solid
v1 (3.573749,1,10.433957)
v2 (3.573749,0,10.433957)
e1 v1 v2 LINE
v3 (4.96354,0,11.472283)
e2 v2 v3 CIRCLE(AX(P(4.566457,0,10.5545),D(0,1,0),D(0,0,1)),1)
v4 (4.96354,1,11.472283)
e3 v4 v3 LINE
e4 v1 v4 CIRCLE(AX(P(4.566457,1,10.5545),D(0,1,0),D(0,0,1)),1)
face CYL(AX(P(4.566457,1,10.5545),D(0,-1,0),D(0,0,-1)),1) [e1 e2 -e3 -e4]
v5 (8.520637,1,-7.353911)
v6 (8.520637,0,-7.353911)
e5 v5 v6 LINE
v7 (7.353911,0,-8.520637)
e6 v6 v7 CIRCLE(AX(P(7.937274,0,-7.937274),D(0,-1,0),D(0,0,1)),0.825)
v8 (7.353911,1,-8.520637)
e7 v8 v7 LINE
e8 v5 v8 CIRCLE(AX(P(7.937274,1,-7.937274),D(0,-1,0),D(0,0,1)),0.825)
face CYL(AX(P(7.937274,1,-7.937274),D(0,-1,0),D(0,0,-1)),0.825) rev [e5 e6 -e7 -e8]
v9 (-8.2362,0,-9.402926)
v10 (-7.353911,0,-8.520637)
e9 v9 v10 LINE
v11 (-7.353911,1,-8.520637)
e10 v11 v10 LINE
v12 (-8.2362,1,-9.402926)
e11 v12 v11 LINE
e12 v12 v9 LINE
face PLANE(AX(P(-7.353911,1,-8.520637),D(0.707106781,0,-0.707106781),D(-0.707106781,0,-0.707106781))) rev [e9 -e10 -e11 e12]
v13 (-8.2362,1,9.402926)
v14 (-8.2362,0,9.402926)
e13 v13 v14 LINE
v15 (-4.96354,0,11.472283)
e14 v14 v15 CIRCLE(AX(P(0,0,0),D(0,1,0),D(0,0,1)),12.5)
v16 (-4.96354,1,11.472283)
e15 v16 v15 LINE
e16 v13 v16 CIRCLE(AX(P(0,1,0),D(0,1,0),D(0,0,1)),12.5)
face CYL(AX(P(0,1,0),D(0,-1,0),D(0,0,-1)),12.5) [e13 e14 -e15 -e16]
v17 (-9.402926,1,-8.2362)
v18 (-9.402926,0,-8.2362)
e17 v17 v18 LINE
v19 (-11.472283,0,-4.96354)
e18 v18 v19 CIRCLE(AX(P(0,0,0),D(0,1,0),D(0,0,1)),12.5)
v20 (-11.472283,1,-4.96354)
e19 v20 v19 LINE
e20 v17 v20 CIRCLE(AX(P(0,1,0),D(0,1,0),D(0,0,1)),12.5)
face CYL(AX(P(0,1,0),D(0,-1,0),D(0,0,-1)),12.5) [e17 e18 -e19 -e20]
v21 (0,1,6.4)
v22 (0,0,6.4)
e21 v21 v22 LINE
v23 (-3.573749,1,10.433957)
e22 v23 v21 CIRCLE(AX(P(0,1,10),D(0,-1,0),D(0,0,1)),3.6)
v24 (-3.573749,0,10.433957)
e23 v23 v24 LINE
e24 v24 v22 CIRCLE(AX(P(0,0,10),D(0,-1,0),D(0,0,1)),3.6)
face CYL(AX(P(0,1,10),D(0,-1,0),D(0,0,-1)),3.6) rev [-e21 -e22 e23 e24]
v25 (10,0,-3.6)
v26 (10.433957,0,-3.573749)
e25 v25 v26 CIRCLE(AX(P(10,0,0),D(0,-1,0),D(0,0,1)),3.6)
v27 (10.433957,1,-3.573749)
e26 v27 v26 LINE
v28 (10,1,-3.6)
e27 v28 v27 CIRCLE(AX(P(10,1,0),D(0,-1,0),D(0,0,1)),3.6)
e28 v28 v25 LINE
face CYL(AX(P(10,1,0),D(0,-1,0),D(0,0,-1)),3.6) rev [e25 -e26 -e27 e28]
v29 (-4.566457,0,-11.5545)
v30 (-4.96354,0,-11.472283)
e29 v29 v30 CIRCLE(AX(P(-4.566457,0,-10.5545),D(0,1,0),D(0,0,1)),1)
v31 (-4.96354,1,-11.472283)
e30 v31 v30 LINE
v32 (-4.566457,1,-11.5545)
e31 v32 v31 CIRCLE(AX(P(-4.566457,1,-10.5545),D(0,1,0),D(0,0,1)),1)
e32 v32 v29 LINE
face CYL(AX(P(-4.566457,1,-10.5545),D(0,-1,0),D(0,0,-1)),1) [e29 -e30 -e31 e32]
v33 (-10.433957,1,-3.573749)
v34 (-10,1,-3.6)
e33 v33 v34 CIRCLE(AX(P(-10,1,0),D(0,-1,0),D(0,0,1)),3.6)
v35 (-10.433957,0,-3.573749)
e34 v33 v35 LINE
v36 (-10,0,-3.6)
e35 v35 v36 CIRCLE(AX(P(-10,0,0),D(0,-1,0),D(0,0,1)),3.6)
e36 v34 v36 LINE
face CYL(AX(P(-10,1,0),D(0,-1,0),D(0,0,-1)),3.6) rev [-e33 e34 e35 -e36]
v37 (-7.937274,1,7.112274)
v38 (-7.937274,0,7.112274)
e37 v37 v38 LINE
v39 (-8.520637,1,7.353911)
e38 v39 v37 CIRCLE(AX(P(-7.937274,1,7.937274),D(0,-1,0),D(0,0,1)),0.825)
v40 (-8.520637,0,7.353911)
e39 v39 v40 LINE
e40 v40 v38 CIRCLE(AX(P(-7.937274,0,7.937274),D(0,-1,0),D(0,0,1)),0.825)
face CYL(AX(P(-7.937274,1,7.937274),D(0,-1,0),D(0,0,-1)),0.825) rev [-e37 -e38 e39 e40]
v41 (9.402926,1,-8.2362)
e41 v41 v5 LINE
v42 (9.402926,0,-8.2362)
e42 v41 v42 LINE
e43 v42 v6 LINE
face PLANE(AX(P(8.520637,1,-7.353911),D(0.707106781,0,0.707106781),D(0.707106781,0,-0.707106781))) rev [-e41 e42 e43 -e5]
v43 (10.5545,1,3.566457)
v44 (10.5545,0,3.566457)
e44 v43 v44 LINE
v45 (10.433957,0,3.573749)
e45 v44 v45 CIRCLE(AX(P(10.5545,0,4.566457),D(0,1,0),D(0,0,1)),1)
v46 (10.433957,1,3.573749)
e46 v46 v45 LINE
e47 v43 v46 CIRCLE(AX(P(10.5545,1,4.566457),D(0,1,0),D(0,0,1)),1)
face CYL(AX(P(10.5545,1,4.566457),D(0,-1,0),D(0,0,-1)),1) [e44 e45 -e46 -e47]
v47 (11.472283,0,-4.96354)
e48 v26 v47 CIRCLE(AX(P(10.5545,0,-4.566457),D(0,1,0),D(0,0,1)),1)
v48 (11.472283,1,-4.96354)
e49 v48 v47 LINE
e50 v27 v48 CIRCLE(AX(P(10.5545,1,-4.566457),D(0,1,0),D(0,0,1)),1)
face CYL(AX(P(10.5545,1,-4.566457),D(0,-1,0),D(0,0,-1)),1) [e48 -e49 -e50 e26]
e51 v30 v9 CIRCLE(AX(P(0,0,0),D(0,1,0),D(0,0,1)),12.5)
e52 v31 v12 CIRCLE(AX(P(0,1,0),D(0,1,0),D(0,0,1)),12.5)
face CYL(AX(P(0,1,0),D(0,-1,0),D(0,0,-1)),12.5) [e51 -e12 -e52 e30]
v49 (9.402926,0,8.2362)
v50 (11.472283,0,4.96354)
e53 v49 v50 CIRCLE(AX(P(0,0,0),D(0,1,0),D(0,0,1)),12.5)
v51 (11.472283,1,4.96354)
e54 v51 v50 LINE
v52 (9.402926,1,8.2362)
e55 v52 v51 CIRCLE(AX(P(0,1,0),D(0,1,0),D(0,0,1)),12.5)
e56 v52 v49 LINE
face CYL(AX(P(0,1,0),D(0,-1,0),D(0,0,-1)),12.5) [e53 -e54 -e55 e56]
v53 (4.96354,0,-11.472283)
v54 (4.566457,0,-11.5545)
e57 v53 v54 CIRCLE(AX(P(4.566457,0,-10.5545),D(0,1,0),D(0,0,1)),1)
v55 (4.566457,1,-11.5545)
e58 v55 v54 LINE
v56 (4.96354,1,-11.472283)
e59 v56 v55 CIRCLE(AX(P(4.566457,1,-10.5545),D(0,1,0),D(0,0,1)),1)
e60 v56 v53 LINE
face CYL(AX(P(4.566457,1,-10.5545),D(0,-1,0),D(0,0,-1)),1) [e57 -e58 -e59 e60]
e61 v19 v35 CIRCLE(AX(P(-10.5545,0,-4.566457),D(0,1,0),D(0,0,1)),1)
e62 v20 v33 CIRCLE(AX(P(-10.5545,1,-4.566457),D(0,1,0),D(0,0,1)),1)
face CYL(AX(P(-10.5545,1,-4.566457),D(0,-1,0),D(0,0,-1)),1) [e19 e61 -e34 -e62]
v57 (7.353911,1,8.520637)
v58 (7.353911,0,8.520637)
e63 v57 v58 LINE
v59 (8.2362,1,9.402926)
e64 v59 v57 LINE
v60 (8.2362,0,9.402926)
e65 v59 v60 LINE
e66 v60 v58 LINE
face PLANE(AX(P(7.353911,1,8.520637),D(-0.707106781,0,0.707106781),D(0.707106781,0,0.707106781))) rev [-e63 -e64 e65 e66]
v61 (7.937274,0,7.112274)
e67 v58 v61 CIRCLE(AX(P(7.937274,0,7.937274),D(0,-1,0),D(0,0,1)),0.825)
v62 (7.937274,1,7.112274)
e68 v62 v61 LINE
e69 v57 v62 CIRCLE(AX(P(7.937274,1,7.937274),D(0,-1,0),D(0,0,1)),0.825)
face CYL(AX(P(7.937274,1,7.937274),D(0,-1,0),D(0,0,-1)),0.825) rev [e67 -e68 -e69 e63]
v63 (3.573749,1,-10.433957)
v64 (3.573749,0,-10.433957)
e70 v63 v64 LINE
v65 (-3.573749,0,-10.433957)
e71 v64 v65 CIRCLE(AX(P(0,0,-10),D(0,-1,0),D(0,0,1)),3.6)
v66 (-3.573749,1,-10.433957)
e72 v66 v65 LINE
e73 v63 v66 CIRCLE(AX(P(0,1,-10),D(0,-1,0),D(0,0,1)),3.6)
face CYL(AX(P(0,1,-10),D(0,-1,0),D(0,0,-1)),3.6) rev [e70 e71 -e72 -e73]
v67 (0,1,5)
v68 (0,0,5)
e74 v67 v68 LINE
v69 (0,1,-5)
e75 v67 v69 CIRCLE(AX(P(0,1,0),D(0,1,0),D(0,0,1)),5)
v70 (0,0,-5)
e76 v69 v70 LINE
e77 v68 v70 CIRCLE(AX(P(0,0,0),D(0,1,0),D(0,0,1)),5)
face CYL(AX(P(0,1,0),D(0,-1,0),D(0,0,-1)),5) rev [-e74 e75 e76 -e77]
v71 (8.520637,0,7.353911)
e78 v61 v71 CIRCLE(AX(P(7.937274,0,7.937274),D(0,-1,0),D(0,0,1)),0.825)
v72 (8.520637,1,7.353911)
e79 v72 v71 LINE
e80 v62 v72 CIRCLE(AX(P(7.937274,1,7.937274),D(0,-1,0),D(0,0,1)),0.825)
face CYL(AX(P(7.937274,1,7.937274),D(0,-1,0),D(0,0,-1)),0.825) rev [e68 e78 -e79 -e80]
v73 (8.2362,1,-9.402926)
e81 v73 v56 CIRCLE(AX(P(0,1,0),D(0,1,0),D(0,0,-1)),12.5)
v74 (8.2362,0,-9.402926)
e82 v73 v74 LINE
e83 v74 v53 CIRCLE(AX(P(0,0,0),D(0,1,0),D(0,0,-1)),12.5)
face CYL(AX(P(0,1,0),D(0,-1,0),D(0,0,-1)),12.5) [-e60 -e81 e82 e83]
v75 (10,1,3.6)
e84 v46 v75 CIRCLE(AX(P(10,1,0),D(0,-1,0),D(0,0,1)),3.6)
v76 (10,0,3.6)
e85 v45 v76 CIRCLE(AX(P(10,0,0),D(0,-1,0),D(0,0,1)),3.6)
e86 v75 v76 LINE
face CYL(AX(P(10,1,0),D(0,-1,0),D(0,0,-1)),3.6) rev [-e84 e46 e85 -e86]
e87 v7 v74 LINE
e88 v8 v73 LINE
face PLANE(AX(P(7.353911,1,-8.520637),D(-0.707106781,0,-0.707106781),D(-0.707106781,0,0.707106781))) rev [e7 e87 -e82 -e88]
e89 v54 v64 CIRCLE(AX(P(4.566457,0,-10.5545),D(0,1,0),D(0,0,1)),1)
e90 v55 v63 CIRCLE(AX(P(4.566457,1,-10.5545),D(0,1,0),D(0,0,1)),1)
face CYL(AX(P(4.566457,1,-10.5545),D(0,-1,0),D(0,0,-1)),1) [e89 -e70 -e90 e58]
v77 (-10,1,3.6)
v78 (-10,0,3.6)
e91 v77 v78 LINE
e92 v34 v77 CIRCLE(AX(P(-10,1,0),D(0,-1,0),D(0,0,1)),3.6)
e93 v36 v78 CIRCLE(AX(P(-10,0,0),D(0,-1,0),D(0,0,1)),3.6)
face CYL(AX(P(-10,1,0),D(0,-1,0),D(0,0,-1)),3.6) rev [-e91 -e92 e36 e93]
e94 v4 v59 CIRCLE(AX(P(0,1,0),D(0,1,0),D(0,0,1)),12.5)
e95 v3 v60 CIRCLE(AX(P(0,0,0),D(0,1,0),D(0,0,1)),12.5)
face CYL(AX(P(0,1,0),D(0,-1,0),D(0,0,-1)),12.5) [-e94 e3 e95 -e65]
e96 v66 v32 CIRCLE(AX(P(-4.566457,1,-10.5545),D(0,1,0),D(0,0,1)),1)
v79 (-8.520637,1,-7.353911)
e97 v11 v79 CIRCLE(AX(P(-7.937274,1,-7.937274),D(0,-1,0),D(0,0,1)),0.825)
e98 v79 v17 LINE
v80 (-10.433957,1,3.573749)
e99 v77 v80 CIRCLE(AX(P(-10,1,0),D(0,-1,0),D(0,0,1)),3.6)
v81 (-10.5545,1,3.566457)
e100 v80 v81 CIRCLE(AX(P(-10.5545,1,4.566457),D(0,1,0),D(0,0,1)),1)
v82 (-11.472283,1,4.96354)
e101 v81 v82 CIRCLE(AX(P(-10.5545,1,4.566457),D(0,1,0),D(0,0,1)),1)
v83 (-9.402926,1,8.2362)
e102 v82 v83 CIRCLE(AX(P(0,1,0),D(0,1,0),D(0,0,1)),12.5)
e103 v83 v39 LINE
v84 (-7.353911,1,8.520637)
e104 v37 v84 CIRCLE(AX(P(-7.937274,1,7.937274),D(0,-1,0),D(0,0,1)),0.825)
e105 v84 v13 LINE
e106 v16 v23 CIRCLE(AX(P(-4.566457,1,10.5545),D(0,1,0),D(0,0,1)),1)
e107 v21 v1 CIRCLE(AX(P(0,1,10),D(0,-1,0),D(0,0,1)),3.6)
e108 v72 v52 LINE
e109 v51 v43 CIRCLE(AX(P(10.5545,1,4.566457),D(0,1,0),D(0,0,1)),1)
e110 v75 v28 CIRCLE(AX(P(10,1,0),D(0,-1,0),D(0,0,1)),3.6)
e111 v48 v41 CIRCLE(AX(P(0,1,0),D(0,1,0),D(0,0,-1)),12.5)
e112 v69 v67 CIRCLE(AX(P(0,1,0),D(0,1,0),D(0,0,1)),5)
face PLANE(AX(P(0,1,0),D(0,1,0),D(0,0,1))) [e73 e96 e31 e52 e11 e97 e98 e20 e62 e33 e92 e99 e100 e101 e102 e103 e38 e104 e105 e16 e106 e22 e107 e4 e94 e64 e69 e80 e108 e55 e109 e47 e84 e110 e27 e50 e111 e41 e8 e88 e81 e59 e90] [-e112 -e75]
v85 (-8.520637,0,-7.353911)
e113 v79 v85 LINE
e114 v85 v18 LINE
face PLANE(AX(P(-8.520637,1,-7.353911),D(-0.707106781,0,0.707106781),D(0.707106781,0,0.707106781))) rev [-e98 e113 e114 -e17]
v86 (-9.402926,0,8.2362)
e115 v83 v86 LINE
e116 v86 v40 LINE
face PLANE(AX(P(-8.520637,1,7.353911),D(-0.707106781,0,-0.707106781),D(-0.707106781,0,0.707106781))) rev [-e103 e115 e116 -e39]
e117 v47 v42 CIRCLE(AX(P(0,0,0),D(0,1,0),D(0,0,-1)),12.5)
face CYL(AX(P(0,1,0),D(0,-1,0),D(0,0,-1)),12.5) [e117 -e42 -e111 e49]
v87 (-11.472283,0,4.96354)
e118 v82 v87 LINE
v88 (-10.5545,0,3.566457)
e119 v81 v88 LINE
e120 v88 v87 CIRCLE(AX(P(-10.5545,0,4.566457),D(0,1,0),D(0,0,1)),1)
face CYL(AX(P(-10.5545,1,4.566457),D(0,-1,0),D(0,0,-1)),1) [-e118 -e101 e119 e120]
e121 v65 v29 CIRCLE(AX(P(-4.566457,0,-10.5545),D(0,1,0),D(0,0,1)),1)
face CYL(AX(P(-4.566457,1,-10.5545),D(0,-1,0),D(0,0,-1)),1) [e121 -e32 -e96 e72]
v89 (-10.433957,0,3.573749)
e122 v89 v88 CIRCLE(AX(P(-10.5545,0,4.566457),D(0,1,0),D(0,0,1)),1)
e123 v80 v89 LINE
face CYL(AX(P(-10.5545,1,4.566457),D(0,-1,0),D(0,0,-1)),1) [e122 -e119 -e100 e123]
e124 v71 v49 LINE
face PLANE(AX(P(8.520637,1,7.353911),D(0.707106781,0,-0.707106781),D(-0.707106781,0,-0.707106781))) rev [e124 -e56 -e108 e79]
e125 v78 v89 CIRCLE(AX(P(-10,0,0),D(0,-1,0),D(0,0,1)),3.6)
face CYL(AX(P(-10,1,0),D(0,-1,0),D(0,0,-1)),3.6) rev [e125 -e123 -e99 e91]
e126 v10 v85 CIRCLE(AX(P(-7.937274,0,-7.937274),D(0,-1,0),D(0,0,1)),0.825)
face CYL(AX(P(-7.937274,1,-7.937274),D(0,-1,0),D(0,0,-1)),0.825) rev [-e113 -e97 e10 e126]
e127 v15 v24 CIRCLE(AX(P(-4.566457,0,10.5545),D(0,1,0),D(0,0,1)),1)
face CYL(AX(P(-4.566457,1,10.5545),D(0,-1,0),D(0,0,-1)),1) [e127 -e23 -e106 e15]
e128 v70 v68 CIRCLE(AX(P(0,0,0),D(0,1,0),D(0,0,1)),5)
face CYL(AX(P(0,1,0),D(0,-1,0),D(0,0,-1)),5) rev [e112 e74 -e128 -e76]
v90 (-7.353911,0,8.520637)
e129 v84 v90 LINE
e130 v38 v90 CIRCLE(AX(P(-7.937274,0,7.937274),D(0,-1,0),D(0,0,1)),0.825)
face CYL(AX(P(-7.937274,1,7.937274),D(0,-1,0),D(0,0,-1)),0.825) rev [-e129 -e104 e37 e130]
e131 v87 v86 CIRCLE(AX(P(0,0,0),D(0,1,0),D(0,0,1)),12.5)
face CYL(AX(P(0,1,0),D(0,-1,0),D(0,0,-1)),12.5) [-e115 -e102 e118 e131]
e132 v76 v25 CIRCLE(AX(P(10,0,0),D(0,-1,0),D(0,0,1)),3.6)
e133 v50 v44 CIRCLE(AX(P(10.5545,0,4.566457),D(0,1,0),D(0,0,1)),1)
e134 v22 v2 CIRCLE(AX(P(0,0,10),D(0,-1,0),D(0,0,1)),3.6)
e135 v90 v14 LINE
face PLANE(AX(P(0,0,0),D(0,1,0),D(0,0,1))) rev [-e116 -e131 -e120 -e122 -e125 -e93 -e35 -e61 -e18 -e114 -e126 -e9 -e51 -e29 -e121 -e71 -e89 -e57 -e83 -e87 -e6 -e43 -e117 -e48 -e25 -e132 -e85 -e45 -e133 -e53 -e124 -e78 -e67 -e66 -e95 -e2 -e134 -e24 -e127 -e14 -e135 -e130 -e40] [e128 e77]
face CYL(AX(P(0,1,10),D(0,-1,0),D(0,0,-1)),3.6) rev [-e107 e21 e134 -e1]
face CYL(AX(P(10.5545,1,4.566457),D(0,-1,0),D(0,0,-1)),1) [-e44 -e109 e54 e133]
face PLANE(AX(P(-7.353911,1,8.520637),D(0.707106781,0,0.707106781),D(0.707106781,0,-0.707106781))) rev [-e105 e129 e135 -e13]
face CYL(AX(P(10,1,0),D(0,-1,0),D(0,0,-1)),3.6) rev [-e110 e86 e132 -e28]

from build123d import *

# Parameters (mm, degrees)
SKETCH4_R           = 5
BOSS_EXTRUDE1_DEPTH = 1


with BuildPart() as part:
    # Sketch4 → Boss-Extrude1 (new body)
    with BuildSketch(Plane(origin=(0, 0, 0), x_dir=(1, 0, 0), z_dir=(0, 1, 0))):
        with BuildLine():
            Line((-7.353910524, -8.520636713), (-8.236199678, -9.402925867))
            ThreePointArc((-8.236199678, -9.402925867), (-6.68048223, -10.565091442), (-4.963540243, -11.472282609))
            ThreePointArc((-4.963540243, -11.472282609), (-3.967940107, -11.355610167), (-3.573748975, -10.433956522))
            ThreePointArc((-3.573748975, -10.433956522), (0, -6.4), (3.573748975, -10.433956522))
            ThreePointArc((3.573748975, -10.433956522), (3.967940107, -11.355610167), (4.963540243, -11.472282609))
            ThreePointArc((4.963540243, -11.472282609), (6.68048223, -10.565091442), (8.236199678, -9.402925867))
            Line((8.236199678, -9.402925867), (7.353910524, -8.520636713))
            ThreePointArc((7.353910524, -8.520636713), (7.353910524, -7.353910524), (8.520636713, -7.353910524))
            Line((8.520636713, -7.353910524), (9.402925867, -8.236199678))
            ThreePointArc((9.402925867, -8.236199678), (10.565091442, -6.68048223), (11.472282609, -4.963540243))
            ThreePointArc((11.472282609, -4.963540243), (11.355610167, -3.967940107), (10.433956522, -3.573748975))
            ThreePointArc((10.433956522, -3.573748975), (6.4, 0), (10.433956522, 3.573748975))
            ThreePointArc((10.433956522, 3.573748975), (11.355610167, 3.967940107), (11.472282609, 4.963540243))
            ThreePointArc((11.472282609, 4.963540243), (10.565091442, 6.68048223), (9.402925867, 8.236199678))
            Line((9.402925867, 8.236199678), (8.520636713, 7.353910524))
            ThreePointArc((8.520636713, 7.353910524), (7.353910524, 7.353910524), (7.353910524, 8.520636713))
            Line((7.353910524, 8.520636713), (8.236199678, 9.402925867))
            ThreePointArc((8.236199678, 9.402925867), (6.68048223, 10.565091442), (4.963540243, 11.472282609))
            ThreePointArc((4.963540243, 11.472282609), (3.967940107, 11.355610167), (3.573748975, 10.433956522))
            ThreePointArc((3.573748975, 10.433956522), (0, 6.4), (-3.573748975, 10.433956522))
            ThreePointArc((-3.573748975, 10.433956522), (-3.967940107, 11.355610167), (-4.963540243, 11.472282609))
            ThreePointArc((-4.963540243, 11.472282609), (-6.68048223, 10.565091442), (-8.236199678, 9.402925867))
            Line((-8.236199678, 9.402925867), (-7.353910524, 8.520636713))
            ThreePointArc((-7.353910524, 8.520636713), (-7.353910524, 7.353910524), (-8.520636713, 7.353910524))
            Line((-8.520636713, 7.353910524), (-9.402925867, 8.236199678))
            ThreePointArc((-9.402925867, 8.236199678), (-10.565091442, 6.68048223), (-11.472282609, 4.963540243))
            ThreePointArc((-11.472282609, 4.963540243), (-11.355610167, 3.967940107), (-10.433956522, 3.573748975))
            ThreePointArc((-10.433956522, 3.573748975), (-6.4, 0), (-10.433956522, -3.573748975))
            ThreePointArc((-10.433956522, -3.573748975), (-11.355610167, -3.967940107), (-11.472282609, -4.963540243))
            ThreePointArc((-11.472282609, -4.963540243), (-10.565091442, -6.68048223), (-9.402925867, -8.236199678))
            Line((-9.402925867, -8.236199678), (-8.520636713, -7.353910524))
            ThreePointArc((-8.520636713, -7.353910524), (-7.353910524, -7.353910524), (-7.353910524, -8.520636713))
        make_face()
        with Locations(Location((0, 0, 0), (0, 0, 90))):
            Circle(SKETCH4_R, mode=Mode.SUBTRACT)
    extrude(amount=BOSS_EXTRUDE1_DEPTH)


solid = part.part
